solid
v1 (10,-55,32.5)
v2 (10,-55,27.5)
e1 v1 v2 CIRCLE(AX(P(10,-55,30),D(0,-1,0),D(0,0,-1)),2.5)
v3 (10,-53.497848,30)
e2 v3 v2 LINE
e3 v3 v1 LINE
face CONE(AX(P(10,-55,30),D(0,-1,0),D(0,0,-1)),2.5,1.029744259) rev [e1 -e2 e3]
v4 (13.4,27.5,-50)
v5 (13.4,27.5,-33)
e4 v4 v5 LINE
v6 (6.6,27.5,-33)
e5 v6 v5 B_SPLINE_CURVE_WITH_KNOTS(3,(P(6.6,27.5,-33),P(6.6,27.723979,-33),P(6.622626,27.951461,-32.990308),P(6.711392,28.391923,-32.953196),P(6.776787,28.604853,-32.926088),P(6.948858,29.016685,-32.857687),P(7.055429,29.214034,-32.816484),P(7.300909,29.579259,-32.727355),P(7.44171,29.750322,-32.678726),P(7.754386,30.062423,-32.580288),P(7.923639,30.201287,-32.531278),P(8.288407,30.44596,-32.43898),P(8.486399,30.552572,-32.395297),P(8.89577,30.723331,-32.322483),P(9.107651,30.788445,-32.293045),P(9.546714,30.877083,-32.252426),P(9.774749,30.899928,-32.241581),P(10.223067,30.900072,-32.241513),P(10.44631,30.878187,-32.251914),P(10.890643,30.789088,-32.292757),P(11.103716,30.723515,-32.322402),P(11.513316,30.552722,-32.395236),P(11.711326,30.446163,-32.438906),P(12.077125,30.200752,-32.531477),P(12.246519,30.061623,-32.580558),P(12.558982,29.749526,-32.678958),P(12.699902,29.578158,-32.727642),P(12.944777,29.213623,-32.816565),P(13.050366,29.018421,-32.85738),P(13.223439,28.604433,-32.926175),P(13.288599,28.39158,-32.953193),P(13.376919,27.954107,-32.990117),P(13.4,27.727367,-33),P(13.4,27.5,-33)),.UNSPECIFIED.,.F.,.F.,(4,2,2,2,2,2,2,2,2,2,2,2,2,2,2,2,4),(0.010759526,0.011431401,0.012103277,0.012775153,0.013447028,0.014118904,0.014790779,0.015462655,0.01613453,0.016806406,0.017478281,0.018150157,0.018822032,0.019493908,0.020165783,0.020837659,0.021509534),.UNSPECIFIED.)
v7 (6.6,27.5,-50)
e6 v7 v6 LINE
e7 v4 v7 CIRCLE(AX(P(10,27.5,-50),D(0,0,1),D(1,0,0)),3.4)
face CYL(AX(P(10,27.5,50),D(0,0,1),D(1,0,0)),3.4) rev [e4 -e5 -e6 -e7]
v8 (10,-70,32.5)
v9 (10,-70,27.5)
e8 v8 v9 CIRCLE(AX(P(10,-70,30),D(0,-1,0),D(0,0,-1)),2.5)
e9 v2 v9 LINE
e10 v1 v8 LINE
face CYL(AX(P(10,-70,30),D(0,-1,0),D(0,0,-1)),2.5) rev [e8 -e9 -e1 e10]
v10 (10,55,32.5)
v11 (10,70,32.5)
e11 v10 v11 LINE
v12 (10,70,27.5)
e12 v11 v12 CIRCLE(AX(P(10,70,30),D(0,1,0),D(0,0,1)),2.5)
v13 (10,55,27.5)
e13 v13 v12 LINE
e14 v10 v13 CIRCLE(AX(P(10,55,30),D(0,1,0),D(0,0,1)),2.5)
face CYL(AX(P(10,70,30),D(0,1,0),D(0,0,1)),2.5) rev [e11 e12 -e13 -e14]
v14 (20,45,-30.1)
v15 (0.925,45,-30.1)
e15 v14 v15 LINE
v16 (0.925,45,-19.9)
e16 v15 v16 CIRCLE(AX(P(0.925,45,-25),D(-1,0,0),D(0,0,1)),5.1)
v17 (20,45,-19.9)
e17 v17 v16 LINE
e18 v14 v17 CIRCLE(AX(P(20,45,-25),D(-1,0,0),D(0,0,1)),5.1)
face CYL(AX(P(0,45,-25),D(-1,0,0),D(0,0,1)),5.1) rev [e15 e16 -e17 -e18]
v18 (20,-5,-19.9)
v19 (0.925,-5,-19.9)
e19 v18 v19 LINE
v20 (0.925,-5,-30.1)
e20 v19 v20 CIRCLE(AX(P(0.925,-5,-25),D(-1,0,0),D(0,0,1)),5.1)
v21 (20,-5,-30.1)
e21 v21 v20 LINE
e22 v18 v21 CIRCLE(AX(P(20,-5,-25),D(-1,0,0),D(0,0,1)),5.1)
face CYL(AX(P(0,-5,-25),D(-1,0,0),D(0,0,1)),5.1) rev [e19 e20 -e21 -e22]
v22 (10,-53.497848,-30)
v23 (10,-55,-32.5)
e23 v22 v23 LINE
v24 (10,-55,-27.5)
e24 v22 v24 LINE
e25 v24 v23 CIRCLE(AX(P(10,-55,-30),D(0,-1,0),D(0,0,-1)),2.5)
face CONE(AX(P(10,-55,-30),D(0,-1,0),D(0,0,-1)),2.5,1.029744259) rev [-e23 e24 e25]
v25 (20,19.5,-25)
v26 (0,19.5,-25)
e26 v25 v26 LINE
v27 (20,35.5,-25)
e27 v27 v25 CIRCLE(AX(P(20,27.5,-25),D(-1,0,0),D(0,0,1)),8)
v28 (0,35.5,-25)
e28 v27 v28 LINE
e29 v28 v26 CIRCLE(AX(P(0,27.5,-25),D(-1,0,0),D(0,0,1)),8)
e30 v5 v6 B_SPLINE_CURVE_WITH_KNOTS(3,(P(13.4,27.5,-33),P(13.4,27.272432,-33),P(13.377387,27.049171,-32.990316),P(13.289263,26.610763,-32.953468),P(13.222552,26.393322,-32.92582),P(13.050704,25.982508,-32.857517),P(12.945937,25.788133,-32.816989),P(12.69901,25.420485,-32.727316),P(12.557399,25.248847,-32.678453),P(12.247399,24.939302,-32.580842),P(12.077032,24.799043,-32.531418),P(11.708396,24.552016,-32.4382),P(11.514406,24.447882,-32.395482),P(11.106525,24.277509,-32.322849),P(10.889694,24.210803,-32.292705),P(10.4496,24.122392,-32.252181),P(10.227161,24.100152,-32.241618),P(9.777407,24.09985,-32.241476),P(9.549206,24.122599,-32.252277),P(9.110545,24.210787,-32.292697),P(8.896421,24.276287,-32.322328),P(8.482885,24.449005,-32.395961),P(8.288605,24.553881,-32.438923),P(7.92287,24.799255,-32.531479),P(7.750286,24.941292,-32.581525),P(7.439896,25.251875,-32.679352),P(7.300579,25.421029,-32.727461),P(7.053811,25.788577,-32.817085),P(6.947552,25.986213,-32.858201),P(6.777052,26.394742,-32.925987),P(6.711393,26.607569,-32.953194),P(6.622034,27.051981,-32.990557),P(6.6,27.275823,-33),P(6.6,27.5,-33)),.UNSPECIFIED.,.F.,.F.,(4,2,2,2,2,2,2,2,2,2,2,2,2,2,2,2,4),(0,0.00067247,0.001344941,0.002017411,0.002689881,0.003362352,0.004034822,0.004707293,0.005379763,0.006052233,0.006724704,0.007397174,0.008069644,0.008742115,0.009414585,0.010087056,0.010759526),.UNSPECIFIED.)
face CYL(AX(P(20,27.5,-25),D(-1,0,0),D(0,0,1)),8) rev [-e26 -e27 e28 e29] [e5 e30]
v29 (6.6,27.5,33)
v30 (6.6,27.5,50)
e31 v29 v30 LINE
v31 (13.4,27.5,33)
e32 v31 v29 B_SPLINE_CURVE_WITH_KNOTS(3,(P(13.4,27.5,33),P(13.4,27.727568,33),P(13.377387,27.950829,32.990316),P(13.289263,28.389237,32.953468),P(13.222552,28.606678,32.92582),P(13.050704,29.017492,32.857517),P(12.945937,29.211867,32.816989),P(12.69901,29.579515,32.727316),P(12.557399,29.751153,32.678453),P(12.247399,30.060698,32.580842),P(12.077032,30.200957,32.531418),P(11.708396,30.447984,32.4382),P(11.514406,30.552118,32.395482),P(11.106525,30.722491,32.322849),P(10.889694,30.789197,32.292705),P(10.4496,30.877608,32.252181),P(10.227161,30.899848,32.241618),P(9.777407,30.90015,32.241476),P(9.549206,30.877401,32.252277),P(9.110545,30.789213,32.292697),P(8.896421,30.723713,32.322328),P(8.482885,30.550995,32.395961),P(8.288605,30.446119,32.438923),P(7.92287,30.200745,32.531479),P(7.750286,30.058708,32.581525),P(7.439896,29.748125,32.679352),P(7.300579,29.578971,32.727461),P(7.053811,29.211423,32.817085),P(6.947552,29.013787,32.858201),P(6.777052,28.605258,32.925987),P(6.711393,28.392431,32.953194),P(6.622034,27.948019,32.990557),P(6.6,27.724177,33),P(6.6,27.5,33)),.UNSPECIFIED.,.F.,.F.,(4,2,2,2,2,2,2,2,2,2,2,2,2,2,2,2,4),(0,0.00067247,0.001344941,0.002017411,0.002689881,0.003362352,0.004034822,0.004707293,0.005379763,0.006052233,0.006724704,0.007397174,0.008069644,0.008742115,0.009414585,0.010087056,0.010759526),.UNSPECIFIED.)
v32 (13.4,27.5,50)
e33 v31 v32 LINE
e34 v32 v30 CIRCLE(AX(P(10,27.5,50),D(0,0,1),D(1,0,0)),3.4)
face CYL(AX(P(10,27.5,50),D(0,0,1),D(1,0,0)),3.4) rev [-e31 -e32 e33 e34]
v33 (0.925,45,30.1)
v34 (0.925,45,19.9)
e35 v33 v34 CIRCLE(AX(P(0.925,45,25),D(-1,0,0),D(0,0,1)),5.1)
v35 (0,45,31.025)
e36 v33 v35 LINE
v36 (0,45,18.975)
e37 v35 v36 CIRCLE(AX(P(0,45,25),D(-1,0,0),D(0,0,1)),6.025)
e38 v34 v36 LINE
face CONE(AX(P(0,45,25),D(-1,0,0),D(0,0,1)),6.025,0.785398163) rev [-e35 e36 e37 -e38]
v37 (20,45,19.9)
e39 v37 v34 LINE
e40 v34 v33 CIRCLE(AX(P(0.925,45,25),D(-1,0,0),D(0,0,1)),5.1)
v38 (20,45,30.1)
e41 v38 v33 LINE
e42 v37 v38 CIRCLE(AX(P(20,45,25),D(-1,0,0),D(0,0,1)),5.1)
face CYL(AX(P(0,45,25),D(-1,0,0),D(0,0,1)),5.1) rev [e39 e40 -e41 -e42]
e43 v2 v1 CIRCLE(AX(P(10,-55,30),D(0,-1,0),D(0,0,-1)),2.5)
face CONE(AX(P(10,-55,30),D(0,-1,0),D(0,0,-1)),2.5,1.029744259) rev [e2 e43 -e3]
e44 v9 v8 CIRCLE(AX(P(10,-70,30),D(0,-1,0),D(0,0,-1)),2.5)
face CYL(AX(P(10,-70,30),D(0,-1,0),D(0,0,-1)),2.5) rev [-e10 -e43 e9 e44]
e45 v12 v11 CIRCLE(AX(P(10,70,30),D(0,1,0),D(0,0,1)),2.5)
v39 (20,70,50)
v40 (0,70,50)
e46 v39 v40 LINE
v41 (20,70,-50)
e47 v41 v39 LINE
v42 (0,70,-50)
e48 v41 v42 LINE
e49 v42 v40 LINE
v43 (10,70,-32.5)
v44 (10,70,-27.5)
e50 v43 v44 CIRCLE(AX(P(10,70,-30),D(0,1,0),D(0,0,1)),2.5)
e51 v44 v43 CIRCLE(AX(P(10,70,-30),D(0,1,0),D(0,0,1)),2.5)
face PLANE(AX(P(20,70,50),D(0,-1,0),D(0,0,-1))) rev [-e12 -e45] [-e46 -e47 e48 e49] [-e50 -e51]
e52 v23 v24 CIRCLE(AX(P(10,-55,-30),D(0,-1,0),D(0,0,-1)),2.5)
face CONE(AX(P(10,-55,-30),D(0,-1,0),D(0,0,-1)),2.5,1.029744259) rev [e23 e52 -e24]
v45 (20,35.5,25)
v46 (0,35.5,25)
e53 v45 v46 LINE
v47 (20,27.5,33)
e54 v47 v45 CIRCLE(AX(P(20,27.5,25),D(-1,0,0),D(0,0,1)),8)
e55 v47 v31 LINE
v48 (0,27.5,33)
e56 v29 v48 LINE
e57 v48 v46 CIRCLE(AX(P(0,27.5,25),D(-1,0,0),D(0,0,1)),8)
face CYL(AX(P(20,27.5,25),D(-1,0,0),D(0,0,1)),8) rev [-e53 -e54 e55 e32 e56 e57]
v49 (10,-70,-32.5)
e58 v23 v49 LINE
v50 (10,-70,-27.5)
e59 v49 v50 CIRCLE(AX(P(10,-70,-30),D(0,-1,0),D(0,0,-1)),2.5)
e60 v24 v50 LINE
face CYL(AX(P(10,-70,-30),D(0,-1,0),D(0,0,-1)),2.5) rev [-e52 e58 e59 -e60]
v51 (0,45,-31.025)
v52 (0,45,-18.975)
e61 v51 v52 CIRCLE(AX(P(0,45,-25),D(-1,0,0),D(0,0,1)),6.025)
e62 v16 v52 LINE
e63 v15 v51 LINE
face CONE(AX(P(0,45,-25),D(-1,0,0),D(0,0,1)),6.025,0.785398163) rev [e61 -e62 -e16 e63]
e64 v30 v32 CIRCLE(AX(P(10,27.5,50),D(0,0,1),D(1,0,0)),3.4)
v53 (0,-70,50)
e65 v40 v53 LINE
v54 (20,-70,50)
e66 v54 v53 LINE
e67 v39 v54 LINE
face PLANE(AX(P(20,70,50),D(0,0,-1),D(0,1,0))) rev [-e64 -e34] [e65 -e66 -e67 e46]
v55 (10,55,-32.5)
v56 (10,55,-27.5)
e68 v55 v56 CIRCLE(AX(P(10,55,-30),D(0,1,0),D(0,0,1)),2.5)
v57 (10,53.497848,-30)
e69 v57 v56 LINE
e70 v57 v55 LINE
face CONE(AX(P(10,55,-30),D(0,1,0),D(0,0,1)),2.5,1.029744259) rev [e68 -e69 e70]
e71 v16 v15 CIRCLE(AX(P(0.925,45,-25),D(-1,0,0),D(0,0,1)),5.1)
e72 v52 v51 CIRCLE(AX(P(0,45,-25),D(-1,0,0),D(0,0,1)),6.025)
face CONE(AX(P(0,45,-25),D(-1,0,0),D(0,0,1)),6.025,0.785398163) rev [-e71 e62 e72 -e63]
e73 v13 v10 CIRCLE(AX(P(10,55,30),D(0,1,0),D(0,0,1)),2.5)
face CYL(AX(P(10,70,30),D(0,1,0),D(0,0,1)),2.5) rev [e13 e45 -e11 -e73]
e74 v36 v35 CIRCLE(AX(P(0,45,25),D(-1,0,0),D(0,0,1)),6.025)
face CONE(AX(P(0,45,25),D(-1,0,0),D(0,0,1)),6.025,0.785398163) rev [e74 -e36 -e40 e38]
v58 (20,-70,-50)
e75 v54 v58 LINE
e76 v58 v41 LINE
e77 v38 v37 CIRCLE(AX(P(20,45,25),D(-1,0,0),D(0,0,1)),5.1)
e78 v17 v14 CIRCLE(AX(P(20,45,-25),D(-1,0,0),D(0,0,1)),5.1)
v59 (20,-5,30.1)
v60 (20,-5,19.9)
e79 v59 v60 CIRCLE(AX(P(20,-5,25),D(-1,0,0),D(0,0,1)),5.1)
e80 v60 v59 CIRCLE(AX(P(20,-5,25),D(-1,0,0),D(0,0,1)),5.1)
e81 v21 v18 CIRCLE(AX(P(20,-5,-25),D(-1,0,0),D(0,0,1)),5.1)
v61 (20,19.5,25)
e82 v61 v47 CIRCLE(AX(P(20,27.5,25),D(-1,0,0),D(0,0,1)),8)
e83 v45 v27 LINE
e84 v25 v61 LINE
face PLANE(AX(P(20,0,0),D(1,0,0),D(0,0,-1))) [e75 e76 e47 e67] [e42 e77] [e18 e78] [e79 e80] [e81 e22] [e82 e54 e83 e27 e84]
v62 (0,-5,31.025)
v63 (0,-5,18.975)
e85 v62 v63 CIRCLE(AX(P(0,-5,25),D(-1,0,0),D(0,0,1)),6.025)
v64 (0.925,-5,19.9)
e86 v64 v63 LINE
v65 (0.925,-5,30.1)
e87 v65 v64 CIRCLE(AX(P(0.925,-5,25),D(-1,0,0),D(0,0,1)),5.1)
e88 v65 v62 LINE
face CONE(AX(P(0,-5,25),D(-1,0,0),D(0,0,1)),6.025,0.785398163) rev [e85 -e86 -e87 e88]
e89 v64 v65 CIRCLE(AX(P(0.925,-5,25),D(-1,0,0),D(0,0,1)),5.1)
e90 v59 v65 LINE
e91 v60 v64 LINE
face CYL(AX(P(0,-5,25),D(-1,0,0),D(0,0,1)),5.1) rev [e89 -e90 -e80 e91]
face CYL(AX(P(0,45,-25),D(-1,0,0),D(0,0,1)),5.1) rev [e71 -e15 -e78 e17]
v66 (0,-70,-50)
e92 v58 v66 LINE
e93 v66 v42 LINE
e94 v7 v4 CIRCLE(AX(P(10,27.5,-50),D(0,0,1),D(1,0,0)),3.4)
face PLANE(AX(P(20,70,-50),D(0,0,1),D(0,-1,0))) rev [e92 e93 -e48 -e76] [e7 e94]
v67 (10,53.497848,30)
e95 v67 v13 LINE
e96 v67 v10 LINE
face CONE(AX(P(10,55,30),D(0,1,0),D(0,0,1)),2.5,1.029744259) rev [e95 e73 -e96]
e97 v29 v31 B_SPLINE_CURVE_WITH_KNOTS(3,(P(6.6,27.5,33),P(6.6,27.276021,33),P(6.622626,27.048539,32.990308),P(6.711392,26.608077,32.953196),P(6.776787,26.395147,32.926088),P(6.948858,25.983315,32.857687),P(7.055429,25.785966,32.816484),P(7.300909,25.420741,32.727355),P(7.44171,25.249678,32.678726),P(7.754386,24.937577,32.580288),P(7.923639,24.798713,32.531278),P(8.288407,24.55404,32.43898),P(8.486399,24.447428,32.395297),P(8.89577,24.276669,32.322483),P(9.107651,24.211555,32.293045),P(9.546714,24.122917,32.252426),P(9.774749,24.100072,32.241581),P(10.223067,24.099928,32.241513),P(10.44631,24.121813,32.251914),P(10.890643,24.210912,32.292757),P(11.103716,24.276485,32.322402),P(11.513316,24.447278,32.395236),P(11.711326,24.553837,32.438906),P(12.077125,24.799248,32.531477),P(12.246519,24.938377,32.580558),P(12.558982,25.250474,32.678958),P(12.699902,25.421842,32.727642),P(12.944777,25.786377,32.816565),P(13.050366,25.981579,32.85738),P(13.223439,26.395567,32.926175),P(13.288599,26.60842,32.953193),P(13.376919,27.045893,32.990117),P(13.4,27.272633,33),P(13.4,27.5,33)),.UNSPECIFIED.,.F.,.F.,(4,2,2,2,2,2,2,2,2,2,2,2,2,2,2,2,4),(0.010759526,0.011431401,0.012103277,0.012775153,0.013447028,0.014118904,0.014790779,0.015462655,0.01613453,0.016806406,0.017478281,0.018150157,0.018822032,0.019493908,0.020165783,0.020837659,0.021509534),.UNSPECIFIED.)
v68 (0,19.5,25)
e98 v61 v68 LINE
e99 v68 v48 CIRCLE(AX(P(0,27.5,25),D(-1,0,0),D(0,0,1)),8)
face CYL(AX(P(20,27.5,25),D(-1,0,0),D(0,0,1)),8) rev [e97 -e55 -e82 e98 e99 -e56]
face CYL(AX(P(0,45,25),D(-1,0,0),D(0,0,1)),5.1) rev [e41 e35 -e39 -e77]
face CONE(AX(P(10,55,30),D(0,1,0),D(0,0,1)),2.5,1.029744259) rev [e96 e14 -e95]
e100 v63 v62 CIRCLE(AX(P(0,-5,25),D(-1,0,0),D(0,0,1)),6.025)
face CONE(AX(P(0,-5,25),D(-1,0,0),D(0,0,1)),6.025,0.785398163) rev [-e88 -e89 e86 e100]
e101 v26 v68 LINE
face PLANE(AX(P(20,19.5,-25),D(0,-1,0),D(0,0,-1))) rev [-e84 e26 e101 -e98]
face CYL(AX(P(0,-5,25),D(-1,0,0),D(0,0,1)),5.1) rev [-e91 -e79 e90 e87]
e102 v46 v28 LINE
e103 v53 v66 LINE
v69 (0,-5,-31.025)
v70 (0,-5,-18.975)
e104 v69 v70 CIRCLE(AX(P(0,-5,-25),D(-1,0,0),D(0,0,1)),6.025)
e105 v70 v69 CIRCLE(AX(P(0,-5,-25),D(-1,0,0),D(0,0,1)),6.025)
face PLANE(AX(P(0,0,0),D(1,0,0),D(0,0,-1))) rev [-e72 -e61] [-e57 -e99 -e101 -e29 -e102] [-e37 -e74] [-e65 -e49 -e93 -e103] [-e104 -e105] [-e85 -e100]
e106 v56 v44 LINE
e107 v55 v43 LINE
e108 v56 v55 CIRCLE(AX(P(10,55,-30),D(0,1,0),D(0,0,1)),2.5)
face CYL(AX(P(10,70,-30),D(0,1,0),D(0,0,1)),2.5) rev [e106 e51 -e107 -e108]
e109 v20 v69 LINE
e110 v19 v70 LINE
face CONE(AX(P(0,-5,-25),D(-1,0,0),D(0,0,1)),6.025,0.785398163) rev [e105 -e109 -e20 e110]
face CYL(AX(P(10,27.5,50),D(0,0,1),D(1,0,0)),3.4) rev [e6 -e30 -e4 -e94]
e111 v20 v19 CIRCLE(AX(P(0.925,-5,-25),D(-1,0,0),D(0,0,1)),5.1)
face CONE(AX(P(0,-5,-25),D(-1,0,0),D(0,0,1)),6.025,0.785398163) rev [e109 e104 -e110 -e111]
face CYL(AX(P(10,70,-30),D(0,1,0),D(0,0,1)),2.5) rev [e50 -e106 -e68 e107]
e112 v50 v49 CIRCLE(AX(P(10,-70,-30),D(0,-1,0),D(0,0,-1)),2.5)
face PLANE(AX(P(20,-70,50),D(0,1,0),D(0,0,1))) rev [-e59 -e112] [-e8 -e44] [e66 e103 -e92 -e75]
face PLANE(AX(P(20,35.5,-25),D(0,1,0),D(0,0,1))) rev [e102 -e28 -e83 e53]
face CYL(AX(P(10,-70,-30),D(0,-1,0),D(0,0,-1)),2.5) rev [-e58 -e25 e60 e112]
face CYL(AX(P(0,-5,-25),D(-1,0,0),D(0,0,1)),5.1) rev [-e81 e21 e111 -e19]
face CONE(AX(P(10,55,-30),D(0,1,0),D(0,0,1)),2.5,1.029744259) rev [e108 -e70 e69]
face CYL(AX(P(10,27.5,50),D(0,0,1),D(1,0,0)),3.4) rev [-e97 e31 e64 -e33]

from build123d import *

# Parameters (mm, degrees)
SKETCH_1_W                    = 100
SKETCH_1_H                    = 140
EXTRUDE_1_DEPTH               = 20
HOLE_WIZARD_M6_1_D            = 5
HOLE_WIZARD_M6_1_DEPTH        = 15
HOLE_WIZARD_M6_1_TIP          = 1.502151548
CUT_EXTRUDE_1_DEPTH           = 89.317608663
HOLE_WIZARD_M8_1_D            = 6.8
HOLE_WIZARD_M12_1_D           = 10.2
HOLE_WIZARD_M12_1_CSINK_D     = 12.05
HOLE_WIZARD_M12_1_CSINK_ANGLE = 90
HOLE_WIZARD_M6_2_D            = 5
HOLE_WIZARD_M6_2_DEPTH        = 15
HOLE_WIZARD_M6_2_TIP          = 1.502151548


with BuildPart() as part:
    # 草图1 → 凸台-拉伸1 (new body)
    with BuildSketch(Plane(origin=(0, 0, 0), x_dir=(0, 0, -1), z_dir=(1, 0, 0))):
        Rectangle(SKETCH_1_W, SKETCH_1_H)
    extrude(amount=EXTRUDE_1_DEPTH)

    # M6 螺纹孔1
    with Locations(Plane(origin=(0, -70, 0), x_dir=(-1, 0, 0), z_dir=(0, -1, 0))):
        with Locations((-10, 30), (-10, -30)):
            Hole(HOLE_WIZARD_M6_1_D / 2, depth=HOLE_WIZARD_M6_1_DEPTH)
            with Locations((0, 0, -(HOLE_WIZARD_M6_1_DEPTH + HOLE_WIZARD_M6_1_TIP / 2))):  # 118° drill point
                Cone(0, HOLE_WIZARD_M6_1_D / 2, HOLE_WIZARD_M6_1_TIP, mode=Mode.SUBTRACT)

    # 草图4 → 切除-拉伸1 (cut, through all)
    with BuildSketch(Plane.ZY):
        with BuildLine():
            Line((-25, 35.5), (25, 35.5))
            ThreePointArc((25, 35.5), (33, 27.5), (25, 19.5))
            Line((25, 19.5), (-25, 19.5))
            ThreePointArc((-25, 19.5), (-33, 27.5), (-25, 35.5))
        make_face()
    extrude(amount=-CUT_EXTRUDE_1_DEPTH, mode=Mode.SUBTRACT)

    # M8 螺纹孔1 (through all)
    with Locations(Plane.XY.offset(50)):
        with Locations((10, 27.5)):
            Hole(HOLE_WIZARD_M8_1_D / 2)

    # M12 螺纹孔1 (through all)
    with Locations(Plane.ZY):
        with Locations((-25, 45), (25, 45), (-25, -5), (25, -5)):
            CounterSinkHole(HOLE_WIZARD_M12_1_D / 2, HOLE_WIZARD_M12_1_CSINK_D / 2, counter_sink_angle=HOLE_WIZARD_M12_1_CSINK_ANGLE)

    # M6 螺纹孔2
    with Locations(Plane(origin=(0, 70, 0), x_dir=(1, 0, 0), z_dir=(0, 1, 0))):
        with Locations((10, 30), (10, -30)):
            Hole(HOLE_WIZARD_M6_2_D / 2, depth=HOLE_WIZARD_M6_2_DEPTH)
            with Locations((0, 0, -(HOLE_WIZARD_M6_2_DEPTH + HOLE_WIZARD_M6_2_TIP / 2))):  # 118° drill point
                Cone(0, HOLE_WIZARD_M6_2_D / 2, HOLE_WIZARD_M6_2_TIP, mode=Mode.SUBTRACT)


solid = part.part
